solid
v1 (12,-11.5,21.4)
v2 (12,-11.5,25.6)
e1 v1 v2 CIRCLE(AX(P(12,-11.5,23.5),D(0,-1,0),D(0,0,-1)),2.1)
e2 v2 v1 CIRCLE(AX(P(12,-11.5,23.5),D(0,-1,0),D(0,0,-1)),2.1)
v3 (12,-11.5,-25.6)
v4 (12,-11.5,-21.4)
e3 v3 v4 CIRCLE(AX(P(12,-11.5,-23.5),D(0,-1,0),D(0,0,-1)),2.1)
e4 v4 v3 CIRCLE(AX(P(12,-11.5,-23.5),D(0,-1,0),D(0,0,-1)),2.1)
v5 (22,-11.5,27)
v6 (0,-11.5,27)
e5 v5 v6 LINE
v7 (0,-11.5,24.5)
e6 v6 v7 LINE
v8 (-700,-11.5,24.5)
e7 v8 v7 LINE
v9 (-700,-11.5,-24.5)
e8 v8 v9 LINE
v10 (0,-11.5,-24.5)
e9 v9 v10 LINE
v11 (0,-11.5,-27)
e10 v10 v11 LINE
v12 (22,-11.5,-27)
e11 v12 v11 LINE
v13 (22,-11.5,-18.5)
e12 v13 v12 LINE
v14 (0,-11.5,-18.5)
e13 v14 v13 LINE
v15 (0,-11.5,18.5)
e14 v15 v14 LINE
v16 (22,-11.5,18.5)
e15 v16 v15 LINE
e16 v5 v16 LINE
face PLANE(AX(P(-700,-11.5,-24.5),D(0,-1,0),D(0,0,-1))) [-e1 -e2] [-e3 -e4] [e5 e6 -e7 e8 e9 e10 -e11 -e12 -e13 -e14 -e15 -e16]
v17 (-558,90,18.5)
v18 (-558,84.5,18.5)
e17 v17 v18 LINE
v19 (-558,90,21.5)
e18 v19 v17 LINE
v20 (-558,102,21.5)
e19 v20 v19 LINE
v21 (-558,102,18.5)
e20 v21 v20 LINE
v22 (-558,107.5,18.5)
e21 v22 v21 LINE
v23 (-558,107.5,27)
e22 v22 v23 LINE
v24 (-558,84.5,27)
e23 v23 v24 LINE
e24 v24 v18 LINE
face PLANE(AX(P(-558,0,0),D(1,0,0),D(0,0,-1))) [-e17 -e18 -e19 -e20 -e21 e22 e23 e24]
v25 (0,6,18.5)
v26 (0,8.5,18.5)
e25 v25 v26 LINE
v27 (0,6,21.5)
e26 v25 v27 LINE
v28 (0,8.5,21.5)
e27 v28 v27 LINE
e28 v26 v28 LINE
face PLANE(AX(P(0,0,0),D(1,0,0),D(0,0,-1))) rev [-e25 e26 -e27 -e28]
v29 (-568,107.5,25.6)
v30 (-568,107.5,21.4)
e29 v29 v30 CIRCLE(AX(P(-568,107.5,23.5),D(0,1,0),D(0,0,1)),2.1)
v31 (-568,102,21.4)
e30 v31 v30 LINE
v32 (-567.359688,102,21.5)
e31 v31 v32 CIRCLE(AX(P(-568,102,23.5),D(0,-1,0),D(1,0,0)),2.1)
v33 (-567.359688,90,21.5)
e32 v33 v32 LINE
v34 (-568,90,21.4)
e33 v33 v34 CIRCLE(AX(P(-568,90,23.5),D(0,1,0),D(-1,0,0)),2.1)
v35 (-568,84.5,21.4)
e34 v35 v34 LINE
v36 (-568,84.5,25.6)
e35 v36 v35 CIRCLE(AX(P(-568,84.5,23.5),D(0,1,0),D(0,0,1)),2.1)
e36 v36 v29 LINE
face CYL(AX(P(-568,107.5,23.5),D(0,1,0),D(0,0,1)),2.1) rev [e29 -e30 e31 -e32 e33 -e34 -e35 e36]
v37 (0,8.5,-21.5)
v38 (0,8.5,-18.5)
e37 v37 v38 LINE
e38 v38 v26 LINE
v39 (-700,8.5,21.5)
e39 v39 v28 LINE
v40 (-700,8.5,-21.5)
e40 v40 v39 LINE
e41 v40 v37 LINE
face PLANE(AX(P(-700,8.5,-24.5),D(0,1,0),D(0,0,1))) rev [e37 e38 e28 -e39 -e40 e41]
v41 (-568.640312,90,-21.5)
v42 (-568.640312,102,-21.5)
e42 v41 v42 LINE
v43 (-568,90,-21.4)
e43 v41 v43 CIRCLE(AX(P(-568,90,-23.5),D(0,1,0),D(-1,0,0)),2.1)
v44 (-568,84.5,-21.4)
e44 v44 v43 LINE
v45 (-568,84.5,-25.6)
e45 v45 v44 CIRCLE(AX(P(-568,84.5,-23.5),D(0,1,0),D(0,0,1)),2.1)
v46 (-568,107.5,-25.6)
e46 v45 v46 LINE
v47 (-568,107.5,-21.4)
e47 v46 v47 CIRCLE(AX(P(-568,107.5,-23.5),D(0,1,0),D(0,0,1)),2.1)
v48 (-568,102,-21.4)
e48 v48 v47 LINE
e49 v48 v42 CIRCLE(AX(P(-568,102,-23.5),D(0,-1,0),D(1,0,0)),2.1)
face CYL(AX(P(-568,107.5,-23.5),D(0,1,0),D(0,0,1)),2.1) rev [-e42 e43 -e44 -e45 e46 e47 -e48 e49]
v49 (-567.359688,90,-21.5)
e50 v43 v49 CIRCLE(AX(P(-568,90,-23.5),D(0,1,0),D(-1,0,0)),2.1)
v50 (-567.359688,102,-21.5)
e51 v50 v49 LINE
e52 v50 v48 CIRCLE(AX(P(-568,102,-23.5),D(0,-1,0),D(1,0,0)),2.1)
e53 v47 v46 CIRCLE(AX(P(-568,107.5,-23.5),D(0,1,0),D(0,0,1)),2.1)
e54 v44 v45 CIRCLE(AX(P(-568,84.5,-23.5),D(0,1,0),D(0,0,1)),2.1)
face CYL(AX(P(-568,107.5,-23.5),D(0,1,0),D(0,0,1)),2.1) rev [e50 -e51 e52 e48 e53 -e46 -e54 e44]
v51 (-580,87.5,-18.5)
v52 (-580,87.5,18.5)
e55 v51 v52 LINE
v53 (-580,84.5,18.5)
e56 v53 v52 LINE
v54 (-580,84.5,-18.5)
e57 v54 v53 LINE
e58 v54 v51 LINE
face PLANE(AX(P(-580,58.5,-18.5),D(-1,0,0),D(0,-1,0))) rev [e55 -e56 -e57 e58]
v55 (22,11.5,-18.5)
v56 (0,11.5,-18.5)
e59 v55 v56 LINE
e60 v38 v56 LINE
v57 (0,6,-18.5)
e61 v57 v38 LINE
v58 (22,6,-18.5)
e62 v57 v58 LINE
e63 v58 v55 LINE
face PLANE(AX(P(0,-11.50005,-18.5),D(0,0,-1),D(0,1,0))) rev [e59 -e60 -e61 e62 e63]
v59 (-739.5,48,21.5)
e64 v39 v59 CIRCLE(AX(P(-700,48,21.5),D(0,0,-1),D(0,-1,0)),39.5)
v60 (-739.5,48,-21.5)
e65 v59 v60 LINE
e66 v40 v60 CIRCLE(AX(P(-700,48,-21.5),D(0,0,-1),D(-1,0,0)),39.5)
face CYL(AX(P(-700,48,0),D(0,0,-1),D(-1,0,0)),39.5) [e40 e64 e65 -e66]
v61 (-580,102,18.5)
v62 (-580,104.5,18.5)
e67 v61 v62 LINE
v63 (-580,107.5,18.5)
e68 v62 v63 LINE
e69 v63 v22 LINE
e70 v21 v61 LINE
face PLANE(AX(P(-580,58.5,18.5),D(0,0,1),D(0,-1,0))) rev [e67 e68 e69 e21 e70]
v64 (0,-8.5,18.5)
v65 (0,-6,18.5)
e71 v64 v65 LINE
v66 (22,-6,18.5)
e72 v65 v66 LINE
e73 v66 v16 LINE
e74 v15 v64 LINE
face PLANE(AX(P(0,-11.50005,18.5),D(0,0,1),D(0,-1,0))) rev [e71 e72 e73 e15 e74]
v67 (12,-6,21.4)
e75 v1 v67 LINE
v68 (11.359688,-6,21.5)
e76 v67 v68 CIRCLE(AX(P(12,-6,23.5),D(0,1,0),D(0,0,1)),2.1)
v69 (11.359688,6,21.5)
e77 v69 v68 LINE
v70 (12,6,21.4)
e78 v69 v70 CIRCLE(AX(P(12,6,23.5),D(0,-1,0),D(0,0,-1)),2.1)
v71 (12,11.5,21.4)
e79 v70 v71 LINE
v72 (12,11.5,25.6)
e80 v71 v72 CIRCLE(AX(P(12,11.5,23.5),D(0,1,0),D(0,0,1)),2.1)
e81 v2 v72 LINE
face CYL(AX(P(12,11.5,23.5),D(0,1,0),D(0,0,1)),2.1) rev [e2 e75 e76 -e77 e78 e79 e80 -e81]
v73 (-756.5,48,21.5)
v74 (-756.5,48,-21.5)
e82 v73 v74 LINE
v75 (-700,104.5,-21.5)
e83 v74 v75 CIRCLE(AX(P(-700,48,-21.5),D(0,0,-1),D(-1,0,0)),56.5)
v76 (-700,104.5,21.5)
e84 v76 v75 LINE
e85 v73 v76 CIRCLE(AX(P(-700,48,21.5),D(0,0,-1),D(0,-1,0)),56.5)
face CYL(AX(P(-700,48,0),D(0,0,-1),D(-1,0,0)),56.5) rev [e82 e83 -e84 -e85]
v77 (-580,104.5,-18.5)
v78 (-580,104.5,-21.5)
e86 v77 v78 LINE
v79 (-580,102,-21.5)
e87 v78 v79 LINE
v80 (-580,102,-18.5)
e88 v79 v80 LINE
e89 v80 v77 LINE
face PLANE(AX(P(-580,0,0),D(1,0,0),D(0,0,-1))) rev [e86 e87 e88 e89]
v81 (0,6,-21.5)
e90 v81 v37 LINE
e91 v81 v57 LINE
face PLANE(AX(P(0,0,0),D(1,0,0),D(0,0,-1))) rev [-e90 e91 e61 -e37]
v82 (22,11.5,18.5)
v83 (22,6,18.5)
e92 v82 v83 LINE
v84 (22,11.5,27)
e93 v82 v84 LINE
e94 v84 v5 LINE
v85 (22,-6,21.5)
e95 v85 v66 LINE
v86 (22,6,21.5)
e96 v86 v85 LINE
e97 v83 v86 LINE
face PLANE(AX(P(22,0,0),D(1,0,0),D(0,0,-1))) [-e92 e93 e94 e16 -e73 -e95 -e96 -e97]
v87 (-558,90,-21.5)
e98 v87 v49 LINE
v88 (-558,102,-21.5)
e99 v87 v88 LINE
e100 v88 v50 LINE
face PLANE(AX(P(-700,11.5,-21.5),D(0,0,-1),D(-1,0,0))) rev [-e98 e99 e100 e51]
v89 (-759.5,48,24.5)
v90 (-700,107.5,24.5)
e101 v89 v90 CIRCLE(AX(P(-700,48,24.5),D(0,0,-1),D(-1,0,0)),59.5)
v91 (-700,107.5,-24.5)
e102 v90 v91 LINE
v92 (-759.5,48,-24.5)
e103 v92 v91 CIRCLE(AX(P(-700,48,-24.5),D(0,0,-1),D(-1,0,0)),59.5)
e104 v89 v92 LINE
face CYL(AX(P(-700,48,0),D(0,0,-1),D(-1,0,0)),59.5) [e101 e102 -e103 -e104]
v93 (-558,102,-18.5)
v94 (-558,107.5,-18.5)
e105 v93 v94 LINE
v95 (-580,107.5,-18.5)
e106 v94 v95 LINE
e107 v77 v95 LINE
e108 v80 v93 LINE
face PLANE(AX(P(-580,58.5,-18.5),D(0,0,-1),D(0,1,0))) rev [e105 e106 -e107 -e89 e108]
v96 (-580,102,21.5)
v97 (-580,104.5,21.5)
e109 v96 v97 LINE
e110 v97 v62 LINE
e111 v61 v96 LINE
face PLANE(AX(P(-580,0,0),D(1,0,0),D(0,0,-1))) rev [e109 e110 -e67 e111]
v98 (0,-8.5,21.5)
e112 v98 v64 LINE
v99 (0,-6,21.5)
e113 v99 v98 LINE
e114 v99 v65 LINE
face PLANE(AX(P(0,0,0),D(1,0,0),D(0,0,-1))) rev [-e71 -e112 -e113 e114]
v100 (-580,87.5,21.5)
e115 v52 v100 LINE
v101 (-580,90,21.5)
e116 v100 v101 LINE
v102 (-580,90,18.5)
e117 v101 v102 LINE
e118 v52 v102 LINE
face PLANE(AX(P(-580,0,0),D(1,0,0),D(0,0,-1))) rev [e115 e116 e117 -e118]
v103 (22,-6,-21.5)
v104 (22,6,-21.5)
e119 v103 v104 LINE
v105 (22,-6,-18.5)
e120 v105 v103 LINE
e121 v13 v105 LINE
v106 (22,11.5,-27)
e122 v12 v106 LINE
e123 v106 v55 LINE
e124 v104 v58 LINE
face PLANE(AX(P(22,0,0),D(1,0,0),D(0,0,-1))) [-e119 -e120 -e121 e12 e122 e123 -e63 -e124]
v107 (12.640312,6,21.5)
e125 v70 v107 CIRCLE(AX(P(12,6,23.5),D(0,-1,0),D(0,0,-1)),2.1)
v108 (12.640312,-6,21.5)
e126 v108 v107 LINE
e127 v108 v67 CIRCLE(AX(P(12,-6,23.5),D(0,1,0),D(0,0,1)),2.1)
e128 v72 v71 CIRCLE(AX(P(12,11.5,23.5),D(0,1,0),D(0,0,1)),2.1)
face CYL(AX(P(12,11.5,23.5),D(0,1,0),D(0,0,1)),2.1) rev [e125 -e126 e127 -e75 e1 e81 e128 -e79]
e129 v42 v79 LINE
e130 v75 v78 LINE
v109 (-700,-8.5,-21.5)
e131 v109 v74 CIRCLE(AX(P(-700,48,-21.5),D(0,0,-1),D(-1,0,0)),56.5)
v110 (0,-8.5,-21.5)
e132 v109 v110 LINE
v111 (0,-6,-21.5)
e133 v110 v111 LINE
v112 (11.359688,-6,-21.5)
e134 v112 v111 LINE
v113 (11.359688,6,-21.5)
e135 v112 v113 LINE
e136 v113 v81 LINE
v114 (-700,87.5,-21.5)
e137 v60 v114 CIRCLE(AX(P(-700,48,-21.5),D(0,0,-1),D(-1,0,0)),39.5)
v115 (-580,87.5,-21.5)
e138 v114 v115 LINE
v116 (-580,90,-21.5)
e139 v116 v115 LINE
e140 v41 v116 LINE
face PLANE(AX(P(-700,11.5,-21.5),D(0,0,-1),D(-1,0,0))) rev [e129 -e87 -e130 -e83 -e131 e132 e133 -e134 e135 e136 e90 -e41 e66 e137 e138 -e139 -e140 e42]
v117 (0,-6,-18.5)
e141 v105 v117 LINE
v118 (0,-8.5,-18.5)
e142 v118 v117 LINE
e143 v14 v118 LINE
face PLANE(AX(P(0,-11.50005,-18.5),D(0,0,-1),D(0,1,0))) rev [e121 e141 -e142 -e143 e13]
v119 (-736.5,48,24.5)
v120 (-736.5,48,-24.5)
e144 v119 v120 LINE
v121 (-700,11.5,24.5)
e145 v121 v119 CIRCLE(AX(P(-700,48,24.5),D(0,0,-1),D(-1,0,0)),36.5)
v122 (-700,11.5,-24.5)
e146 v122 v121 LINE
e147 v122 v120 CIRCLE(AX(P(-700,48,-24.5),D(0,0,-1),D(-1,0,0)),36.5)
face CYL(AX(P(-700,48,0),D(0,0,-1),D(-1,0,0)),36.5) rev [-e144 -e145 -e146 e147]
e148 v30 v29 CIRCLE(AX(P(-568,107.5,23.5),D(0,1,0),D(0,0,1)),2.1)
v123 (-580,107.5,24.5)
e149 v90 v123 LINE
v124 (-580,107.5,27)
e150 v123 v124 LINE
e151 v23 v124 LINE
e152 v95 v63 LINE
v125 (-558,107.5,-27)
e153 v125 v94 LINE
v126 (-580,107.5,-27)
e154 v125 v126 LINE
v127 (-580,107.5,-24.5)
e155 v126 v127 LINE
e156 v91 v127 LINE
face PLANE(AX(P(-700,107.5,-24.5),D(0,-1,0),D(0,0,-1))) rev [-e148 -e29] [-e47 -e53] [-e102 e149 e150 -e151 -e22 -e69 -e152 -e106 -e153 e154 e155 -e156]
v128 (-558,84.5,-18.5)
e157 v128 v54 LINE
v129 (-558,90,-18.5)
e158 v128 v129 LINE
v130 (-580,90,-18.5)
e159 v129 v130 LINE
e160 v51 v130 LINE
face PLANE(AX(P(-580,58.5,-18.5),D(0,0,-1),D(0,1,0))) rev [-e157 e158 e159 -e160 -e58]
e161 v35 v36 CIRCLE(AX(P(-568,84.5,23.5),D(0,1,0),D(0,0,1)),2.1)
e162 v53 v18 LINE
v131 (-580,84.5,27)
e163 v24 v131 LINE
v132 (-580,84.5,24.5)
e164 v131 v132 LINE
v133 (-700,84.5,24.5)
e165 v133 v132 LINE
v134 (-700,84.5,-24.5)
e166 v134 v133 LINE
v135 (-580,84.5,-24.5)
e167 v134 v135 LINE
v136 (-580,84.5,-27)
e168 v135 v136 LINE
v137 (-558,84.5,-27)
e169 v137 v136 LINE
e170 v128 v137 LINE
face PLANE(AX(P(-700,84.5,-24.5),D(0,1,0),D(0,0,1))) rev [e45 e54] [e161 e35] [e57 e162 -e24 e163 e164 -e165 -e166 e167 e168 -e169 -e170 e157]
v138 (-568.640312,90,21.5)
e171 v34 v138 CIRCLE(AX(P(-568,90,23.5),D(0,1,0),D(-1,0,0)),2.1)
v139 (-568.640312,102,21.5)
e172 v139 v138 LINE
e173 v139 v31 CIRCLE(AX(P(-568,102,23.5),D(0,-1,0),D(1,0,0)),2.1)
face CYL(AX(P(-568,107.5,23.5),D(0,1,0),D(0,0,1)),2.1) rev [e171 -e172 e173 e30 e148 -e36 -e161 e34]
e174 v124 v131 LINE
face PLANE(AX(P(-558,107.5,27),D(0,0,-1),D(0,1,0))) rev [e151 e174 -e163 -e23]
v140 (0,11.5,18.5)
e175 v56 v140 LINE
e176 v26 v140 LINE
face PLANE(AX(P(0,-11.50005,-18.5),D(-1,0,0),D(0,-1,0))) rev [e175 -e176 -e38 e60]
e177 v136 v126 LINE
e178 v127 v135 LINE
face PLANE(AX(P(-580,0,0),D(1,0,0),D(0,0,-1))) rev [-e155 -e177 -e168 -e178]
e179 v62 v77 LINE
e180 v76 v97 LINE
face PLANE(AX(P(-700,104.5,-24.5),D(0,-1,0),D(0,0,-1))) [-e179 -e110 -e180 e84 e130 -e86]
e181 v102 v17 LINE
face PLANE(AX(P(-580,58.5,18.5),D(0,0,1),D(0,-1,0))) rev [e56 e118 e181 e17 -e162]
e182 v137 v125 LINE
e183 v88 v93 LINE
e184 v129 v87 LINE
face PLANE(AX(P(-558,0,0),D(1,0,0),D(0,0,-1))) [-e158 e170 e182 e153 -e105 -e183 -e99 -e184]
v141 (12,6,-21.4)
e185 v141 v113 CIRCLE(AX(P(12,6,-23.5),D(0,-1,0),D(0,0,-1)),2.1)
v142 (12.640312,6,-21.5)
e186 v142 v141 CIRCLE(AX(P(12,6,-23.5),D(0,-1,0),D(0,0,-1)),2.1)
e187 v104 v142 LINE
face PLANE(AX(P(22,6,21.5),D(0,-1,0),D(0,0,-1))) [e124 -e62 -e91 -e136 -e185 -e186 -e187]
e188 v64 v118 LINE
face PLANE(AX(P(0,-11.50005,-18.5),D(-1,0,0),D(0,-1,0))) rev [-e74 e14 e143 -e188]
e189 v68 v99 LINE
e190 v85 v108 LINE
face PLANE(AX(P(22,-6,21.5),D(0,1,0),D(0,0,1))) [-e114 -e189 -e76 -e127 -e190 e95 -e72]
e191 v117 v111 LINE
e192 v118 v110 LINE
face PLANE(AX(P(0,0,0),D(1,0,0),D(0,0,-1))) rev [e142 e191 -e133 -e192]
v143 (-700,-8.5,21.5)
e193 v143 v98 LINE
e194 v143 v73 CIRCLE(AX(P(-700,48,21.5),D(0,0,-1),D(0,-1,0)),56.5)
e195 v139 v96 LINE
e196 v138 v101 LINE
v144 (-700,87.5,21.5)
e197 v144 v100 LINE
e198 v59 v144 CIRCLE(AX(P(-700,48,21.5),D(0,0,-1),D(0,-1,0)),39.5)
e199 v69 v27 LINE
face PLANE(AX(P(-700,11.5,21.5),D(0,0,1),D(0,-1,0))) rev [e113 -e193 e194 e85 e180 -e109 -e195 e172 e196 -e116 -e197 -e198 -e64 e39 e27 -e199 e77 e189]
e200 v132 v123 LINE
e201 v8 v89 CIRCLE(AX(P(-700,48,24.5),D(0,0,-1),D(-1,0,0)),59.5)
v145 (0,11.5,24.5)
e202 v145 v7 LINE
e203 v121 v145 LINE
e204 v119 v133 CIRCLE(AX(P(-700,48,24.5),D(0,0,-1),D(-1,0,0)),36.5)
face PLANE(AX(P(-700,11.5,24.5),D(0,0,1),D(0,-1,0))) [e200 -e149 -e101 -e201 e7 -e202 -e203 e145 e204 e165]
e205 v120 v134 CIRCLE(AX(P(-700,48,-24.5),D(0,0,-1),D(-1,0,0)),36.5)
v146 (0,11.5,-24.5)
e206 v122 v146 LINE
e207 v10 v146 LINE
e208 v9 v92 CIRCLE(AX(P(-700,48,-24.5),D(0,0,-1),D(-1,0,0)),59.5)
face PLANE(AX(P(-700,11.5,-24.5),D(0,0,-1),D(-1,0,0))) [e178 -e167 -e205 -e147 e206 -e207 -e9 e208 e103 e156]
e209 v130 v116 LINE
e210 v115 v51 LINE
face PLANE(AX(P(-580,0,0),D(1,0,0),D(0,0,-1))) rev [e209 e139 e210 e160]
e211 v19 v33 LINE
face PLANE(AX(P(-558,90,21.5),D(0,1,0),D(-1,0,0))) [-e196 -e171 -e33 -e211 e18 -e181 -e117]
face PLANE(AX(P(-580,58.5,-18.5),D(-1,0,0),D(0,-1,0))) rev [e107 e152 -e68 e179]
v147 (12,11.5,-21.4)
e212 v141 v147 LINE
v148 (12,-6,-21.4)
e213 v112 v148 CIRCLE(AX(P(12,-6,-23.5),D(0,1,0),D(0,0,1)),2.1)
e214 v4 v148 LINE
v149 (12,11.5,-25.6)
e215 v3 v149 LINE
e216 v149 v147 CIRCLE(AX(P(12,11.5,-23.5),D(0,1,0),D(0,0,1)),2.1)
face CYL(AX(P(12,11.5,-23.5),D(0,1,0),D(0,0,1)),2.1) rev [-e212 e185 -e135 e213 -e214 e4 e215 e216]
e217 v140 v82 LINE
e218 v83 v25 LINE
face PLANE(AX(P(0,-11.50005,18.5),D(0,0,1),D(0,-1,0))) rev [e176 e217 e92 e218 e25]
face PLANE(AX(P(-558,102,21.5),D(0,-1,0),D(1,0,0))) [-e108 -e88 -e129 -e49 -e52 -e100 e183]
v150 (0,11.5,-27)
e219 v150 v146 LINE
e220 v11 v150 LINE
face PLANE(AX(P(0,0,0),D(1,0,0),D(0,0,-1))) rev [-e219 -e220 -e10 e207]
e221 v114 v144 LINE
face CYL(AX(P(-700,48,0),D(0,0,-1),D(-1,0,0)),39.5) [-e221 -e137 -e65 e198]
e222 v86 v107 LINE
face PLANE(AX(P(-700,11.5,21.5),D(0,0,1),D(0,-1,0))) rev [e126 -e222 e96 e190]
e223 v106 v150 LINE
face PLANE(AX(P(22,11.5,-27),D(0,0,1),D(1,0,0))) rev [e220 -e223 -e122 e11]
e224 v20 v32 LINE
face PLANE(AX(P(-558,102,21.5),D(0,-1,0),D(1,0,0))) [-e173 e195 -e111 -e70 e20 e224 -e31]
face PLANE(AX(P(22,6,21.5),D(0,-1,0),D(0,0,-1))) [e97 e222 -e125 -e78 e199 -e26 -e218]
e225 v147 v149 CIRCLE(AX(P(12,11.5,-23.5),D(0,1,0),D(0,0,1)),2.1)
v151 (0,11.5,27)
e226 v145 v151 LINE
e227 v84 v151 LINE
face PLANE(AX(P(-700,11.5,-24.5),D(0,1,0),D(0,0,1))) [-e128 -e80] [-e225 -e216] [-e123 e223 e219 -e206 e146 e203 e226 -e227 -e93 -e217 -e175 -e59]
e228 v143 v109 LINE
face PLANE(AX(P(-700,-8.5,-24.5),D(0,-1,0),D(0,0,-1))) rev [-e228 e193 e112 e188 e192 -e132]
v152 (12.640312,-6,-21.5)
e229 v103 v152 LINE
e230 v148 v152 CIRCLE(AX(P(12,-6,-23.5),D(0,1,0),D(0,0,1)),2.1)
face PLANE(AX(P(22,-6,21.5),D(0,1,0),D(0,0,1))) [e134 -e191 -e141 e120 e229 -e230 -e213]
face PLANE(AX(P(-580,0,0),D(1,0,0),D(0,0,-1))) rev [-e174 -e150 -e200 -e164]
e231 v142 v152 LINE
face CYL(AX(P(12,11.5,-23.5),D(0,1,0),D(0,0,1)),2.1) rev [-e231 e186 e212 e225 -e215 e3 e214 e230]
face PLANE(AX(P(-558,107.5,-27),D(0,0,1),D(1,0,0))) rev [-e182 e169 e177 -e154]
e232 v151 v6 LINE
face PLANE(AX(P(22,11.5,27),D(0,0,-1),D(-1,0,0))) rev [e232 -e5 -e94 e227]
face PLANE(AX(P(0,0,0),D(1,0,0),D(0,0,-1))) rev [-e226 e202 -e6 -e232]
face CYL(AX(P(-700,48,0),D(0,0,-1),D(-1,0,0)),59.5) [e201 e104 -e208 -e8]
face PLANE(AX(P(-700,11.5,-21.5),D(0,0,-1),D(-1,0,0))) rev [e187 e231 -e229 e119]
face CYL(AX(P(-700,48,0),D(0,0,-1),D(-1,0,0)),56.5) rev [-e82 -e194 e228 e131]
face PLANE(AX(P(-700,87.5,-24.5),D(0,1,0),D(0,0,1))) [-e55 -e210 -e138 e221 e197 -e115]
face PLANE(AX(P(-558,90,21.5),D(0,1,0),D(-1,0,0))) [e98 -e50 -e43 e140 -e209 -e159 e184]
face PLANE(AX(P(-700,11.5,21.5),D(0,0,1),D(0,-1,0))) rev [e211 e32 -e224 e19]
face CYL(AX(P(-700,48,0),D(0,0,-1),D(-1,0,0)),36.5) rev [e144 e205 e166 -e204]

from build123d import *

# Parameters (mm, degrees)
SKETCH_2_W                  = 49
SKETCH_2_H                  = 23
SHELL_1_T                   = -3
SKETCH_11_W                 = 54
SKETCH_11_H                 = 23
SKETCH_11_W_2               = 43
SKETCH_11_H_2               = 12
EXTRUDE_1_DEPTH             = 22
SKETCH_12_W                 = 23.011901601
SKETCH_12_H                 = 37
CUT_EXTRUDE_9_DEPTH         = 767.019092451
HOLE_WIZARD_4_2_4_2_1_D     = 4.2
SKETCH_15_W                 = 54
SKETCH_15_H                 = 23
SKETCH_15_W_2               = 43
SKETCH_15_H_2               = 12
EXTRUDE_2_DEPTH             = 22
SKETCH_16_W                 = 45.795478168
SKETCH_16_H                 = 37
CUT_EXTRUDE_10_DEPTH        = 49
HOLE_WIZARD_4_2_4_2_2_D     = 4.2
HOLE_WIZARD_4_2_4_2_2_DEPTH = 50
HOLE_WIZARD_4_2_4_2_2_TIP   = 1.2618073


with BuildPart() as part:
    # 扫描1: sweep along a path in 草图1
    with BuildLine(Plane.XY) as sweep_1_path:
        Line((0, 0), (-700, 0))
        ThreePointArc((-700, 0), (-748, 48), (-700, 96))
        Line((-700, 96), (-580, 96))
    # 草图2 → 扫描1 (sweep)
    with BuildSketch(Plane(origin=(0, 0, 0), x_dir=(0, 0, -1), z_dir=(1, 0, 0))):
        Rectangle(SKETCH_2_W, SKETCH_2_H)
    sweep(path=sweep_1_path.line)

    # 抽壳1
    shell_1_openings = [part.faces().sort_by_distance(p)[0] for p in [
        (-580, 96, 0),
        (0, 0, 0),
    ]]
    offset(amount=SHELL_1_T, openings=shell_1_openings, kind=Kind.INTERSECTION)

    # 草图11 → 凸台-拉伸1 (add)
    with BuildSketch(Plane(origin=(0, 0, 0), x_dir=(0, 0, -1), z_dir=(1, 0, 0))):
        Rectangle(SKETCH_11_W, SKETCH_11_H)
        Rectangle(SKETCH_11_W_2, SKETCH_11_H_2, mode=Mode.SUBTRACT)
    extrude(amount=EXTRUDE_1_DEPTH)

    # 草图12 → 切除-拉伸9 (cut, through all)
    with BuildSketch(Plane(origin=(0, 11.5, 0), x_dir=(1, 0, 0), z_dir=(0, 1, 0))):
        with Locations((11.505950801, 0)):
            Rectangle(SKETCH_12_W, SKETCH_12_H)
    extrude(amount=-CUT_EXTRUDE_9_DEPTH, mode=Mode.SUBTRACT)

    # Ø4.2 (4.2) 直径孔1 (through all)
    with Locations(Plane(origin=(0, 11.5, 0), x_dir=(1, 0, 0), z_dir=(0, 1, 0))):
        with Locations((12, 23.5), (12, -23.5)):
            Hole(HOLE_WIZARD_4_2_4_2_1_D / 2)

    # 草图15 → 凸台-拉伸2 (add)
    with BuildSketch(Plane(origin=(-580, 0, 0), x_dir=(0, 0, -1), z_dir=(1, 0, 0))):
        with Locations((0, 96)):
            Rectangle(SKETCH_15_W, SKETCH_15_H)
        with Locations((0, 96)):
            Rectangle(SKETCH_15_W_2, SKETCH_15_H_2, mode=Mode.SUBTRACT)
    extrude(amount=EXTRUDE_2_DEPTH)

    # 草图16 → 切除-拉伸10 (cut)
    with BuildSketch(Plane(origin=(0, 107.5, 0), x_dir=(1, 0, 0), z_dir=(0, 1, 0))):
        with Locations((-557.102260916, 0)):
            Rectangle(SKETCH_16_W, SKETCH_16_H)
    extrude(amount=-CUT_EXTRUDE_10_DEPTH, mode=Mode.SUBTRACT)

    # Ø4.2 (4.2) 直径孔2
    with Locations(Plane(origin=(0, 107.5, 0), x_dir=(1, 0, 0), z_dir=(0, 1, 0))):
        with Locations((-568, 23.5), (-568, -23.5)):
            Hole(HOLE_WIZARD_4_2_4_2_2_D / 2, depth=HOLE_WIZARD_4_2_4_2_2_DEPTH)
            with Locations((0, 0, -(HOLE_WIZARD_4_2_4_2_2_DEPTH + HOLE_WIZARD_4_2_4_2_2_TIP / 2))):  # 118° drill point
                Cone(0, HOLE_WIZARD_4_2_4_2_2_D / 2, HOLE_WIZARD_4_2_4_2_2_TIP, mode=Mode.SUBTRACT)


solid = part.part
